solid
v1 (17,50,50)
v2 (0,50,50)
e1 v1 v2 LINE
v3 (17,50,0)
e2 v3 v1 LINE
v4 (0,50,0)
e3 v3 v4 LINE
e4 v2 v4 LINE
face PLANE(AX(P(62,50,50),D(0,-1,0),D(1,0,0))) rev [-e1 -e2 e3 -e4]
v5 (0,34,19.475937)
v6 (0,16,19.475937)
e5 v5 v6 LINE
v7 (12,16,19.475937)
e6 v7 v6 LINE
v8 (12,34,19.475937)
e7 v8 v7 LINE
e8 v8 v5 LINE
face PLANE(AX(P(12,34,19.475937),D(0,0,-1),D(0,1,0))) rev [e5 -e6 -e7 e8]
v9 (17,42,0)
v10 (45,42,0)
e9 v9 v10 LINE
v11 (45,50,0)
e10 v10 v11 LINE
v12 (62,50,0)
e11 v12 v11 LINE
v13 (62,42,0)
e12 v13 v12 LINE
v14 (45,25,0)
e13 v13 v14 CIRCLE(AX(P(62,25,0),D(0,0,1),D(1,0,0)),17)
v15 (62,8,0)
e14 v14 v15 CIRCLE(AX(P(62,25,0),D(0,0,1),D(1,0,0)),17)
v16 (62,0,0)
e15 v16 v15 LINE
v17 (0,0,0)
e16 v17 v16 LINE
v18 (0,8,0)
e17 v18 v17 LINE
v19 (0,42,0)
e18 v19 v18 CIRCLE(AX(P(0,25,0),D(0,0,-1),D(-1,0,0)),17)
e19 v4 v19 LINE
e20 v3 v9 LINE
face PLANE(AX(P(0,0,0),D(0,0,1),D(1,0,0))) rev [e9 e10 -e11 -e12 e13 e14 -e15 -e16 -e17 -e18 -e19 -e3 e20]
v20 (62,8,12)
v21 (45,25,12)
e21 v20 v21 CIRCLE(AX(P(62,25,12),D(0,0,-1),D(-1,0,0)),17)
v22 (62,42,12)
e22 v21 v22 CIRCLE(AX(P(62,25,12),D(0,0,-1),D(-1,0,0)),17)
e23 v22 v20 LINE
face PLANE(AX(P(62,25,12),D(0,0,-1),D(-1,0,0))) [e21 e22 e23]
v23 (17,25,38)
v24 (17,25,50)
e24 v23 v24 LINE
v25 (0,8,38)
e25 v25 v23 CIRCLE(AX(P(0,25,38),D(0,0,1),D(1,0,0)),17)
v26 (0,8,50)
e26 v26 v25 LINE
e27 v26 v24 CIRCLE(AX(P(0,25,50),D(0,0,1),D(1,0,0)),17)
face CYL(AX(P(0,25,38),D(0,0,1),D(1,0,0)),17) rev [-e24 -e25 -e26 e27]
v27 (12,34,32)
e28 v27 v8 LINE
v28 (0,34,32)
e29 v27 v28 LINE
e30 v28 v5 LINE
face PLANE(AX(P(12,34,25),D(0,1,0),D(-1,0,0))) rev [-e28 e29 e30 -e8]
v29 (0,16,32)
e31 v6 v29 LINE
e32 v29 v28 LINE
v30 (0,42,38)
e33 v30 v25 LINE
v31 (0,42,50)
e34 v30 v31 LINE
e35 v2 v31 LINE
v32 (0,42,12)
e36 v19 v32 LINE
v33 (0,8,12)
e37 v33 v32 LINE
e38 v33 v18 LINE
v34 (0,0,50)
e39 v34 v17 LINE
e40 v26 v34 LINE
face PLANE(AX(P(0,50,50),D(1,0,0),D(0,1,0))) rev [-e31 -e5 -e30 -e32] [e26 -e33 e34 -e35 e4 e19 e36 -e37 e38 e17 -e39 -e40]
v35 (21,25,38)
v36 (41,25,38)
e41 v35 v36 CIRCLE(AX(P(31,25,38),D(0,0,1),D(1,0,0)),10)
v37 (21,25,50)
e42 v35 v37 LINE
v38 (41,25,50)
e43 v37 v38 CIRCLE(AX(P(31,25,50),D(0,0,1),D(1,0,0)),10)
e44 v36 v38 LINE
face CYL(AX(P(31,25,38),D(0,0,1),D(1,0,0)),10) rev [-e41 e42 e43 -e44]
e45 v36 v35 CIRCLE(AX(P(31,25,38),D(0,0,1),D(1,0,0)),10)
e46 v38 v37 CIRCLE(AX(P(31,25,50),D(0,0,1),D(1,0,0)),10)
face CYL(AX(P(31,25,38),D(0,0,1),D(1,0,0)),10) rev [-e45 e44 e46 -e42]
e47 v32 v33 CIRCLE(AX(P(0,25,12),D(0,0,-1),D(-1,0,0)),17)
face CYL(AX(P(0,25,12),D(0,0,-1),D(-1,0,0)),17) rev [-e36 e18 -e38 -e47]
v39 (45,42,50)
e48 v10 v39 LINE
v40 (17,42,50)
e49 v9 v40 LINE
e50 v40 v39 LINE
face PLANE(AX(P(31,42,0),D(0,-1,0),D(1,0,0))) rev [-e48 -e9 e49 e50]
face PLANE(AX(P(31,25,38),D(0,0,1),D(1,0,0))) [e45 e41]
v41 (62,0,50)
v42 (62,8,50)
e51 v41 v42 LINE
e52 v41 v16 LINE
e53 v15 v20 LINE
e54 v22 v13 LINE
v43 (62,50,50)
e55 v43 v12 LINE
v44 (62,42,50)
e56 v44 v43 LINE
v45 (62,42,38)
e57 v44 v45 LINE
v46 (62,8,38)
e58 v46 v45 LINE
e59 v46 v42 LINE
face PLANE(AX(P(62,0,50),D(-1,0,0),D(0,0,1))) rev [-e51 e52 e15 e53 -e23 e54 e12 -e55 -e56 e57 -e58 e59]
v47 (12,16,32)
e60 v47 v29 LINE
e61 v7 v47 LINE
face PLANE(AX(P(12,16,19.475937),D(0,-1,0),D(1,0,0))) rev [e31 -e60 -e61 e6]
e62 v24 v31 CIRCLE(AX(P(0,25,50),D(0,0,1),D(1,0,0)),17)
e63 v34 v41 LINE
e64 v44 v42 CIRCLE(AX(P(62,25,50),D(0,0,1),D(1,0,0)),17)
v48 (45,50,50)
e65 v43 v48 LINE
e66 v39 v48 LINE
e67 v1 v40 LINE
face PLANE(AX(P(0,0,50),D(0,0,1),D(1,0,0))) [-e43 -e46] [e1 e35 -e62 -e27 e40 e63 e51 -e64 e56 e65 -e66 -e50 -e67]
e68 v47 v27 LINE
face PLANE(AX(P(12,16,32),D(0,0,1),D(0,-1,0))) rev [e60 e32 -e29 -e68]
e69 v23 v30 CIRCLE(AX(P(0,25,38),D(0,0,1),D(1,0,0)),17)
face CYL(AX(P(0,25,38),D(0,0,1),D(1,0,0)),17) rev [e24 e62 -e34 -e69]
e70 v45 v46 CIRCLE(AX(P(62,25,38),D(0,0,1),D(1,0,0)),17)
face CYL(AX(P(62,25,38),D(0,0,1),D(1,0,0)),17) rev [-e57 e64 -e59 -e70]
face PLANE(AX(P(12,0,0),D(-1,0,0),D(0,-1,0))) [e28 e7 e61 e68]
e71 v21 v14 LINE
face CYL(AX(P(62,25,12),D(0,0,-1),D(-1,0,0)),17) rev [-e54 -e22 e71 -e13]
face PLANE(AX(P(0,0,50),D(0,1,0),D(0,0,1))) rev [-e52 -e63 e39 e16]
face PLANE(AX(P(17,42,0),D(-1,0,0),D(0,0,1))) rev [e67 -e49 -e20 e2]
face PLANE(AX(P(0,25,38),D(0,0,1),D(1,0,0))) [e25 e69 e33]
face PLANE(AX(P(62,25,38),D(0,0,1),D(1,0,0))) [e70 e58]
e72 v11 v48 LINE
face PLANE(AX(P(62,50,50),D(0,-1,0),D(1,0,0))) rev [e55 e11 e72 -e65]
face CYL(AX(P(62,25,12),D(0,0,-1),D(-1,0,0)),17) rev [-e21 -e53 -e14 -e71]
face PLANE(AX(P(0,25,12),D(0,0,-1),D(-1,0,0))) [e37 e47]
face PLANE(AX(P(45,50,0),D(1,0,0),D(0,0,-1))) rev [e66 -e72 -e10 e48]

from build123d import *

# Parameters (mm, degrees)
BLOCK_PROFILE_62X50_W             = 62
BLOCK_PROFILE_62X50_H             = 50
BASE_BLOCK_62X50X50_DEPTH         = 50
SQUARE_CUT_A_PROFILE_34X34_R      = 17
SQUARE_CUT_A_34X34_DEPTH_12_DEPTH = 12
SIDE_ARC_CUT_A_DEPTH              = 95.042543564
SIDE_ARC_CUT_B_DEPTH_12_DEPTH     = 12
SQUARE_START                      = -12
SQUARE_CUT_B_PROFILE_34X34_R      = 17
SQUARE_CUT_B_34X34_DEPTH_12_DEPTH = 12
HOLE_PROFILE_20_R                 = 10
HOLE_20_DEPTH_12_DEPTH            = 12


with BuildPart() as part:
    # Block Profile 62x50 → Base Block 62x50x50 (new body)
    with BuildSketch(Plane.XY):
        with Locations((31, 25)):
            Rectangle(BLOCK_PROFILE_62X50_W, BLOCK_PROFILE_62X50_H)
    extrude(amount=BASE_BLOCK_62X50X50_DEPTH)

    # Square Cut A Profile 34x34 → Square Cut A 34x34 Depth 12 (cut)
    with BuildSketch(Plane.XY.offset(50)):
        with Locations((62, 25)):
            Circle(SQUARE_CUT_A_PROFILE_34X34_R)
        with Locations((0, 25)):
            Circle(SQUARE_CUT_A_PROFILE_34X34_R)
    extrude(amount=-SQUARE_CUT_A_34X34_DEPTH_12_DEPTH, mode=Mode.SUBTRACT)

    # Side Arc Cut A Profile → Side Arc Cut A (cut, through all)
    with BuildSketch(Plane.XY.offset(50)):
        Polygon((31, 42), (17, 42), (17, 50), (45, 50), (45, 42), align=None)
    extrude(amount=-SIDE_ARC_CUT_A_DEPTH, mode=Mode.SUBTRACT)

    # Side Arc Cut B Profile → Side Arc Cut B Depth 12 (cut)
    with BuildSketch(Plane.ZY):
        Polygon((25, 34), (19.475936602, 34), (19.475936602, 16), (32, 16), (32, 34), align=None)
    extrude(amount=-SIDE_ARC_CUT_B_DEPTH_12_DEPTH, mode=Mode.SUBTRACT)

    # Square Cut B Profile 34x34 → Square Cut B 34x34 Depth 12 (cut)
    with BuildSketch(Plane(origin=(0, 0, 0), x_dir=(-1, 0, 0), z_dir=(0, 0, -1)).offset(SQUARE_START)):
        with Locations((-62, 25)):
            Circle(SQUARE_CUT_B_PROFILE_34X34_R)
        with Locations((0, 25)):
            Circle(SQUARE_CUT_B_PROFILE_34X34_R)
    extrude(amount=SQUARE_CUT_B_34X34_DEPTH_12_DEPTH, mode=Mode.SUBTRACT)

    # Hole Profile Ø20 → Hole Ø20 Depth 12 (cut)
    with BuildSketch(Plane.XY.offset(50)):
        with Locations((31, 25)):
            Circle(HOLE_PROFILE_20_R)
    extrude(amount=-HOLE_20_DEPTH_12_DEPTH, mode=Mode.SUBTRACT)


solid = part.part
